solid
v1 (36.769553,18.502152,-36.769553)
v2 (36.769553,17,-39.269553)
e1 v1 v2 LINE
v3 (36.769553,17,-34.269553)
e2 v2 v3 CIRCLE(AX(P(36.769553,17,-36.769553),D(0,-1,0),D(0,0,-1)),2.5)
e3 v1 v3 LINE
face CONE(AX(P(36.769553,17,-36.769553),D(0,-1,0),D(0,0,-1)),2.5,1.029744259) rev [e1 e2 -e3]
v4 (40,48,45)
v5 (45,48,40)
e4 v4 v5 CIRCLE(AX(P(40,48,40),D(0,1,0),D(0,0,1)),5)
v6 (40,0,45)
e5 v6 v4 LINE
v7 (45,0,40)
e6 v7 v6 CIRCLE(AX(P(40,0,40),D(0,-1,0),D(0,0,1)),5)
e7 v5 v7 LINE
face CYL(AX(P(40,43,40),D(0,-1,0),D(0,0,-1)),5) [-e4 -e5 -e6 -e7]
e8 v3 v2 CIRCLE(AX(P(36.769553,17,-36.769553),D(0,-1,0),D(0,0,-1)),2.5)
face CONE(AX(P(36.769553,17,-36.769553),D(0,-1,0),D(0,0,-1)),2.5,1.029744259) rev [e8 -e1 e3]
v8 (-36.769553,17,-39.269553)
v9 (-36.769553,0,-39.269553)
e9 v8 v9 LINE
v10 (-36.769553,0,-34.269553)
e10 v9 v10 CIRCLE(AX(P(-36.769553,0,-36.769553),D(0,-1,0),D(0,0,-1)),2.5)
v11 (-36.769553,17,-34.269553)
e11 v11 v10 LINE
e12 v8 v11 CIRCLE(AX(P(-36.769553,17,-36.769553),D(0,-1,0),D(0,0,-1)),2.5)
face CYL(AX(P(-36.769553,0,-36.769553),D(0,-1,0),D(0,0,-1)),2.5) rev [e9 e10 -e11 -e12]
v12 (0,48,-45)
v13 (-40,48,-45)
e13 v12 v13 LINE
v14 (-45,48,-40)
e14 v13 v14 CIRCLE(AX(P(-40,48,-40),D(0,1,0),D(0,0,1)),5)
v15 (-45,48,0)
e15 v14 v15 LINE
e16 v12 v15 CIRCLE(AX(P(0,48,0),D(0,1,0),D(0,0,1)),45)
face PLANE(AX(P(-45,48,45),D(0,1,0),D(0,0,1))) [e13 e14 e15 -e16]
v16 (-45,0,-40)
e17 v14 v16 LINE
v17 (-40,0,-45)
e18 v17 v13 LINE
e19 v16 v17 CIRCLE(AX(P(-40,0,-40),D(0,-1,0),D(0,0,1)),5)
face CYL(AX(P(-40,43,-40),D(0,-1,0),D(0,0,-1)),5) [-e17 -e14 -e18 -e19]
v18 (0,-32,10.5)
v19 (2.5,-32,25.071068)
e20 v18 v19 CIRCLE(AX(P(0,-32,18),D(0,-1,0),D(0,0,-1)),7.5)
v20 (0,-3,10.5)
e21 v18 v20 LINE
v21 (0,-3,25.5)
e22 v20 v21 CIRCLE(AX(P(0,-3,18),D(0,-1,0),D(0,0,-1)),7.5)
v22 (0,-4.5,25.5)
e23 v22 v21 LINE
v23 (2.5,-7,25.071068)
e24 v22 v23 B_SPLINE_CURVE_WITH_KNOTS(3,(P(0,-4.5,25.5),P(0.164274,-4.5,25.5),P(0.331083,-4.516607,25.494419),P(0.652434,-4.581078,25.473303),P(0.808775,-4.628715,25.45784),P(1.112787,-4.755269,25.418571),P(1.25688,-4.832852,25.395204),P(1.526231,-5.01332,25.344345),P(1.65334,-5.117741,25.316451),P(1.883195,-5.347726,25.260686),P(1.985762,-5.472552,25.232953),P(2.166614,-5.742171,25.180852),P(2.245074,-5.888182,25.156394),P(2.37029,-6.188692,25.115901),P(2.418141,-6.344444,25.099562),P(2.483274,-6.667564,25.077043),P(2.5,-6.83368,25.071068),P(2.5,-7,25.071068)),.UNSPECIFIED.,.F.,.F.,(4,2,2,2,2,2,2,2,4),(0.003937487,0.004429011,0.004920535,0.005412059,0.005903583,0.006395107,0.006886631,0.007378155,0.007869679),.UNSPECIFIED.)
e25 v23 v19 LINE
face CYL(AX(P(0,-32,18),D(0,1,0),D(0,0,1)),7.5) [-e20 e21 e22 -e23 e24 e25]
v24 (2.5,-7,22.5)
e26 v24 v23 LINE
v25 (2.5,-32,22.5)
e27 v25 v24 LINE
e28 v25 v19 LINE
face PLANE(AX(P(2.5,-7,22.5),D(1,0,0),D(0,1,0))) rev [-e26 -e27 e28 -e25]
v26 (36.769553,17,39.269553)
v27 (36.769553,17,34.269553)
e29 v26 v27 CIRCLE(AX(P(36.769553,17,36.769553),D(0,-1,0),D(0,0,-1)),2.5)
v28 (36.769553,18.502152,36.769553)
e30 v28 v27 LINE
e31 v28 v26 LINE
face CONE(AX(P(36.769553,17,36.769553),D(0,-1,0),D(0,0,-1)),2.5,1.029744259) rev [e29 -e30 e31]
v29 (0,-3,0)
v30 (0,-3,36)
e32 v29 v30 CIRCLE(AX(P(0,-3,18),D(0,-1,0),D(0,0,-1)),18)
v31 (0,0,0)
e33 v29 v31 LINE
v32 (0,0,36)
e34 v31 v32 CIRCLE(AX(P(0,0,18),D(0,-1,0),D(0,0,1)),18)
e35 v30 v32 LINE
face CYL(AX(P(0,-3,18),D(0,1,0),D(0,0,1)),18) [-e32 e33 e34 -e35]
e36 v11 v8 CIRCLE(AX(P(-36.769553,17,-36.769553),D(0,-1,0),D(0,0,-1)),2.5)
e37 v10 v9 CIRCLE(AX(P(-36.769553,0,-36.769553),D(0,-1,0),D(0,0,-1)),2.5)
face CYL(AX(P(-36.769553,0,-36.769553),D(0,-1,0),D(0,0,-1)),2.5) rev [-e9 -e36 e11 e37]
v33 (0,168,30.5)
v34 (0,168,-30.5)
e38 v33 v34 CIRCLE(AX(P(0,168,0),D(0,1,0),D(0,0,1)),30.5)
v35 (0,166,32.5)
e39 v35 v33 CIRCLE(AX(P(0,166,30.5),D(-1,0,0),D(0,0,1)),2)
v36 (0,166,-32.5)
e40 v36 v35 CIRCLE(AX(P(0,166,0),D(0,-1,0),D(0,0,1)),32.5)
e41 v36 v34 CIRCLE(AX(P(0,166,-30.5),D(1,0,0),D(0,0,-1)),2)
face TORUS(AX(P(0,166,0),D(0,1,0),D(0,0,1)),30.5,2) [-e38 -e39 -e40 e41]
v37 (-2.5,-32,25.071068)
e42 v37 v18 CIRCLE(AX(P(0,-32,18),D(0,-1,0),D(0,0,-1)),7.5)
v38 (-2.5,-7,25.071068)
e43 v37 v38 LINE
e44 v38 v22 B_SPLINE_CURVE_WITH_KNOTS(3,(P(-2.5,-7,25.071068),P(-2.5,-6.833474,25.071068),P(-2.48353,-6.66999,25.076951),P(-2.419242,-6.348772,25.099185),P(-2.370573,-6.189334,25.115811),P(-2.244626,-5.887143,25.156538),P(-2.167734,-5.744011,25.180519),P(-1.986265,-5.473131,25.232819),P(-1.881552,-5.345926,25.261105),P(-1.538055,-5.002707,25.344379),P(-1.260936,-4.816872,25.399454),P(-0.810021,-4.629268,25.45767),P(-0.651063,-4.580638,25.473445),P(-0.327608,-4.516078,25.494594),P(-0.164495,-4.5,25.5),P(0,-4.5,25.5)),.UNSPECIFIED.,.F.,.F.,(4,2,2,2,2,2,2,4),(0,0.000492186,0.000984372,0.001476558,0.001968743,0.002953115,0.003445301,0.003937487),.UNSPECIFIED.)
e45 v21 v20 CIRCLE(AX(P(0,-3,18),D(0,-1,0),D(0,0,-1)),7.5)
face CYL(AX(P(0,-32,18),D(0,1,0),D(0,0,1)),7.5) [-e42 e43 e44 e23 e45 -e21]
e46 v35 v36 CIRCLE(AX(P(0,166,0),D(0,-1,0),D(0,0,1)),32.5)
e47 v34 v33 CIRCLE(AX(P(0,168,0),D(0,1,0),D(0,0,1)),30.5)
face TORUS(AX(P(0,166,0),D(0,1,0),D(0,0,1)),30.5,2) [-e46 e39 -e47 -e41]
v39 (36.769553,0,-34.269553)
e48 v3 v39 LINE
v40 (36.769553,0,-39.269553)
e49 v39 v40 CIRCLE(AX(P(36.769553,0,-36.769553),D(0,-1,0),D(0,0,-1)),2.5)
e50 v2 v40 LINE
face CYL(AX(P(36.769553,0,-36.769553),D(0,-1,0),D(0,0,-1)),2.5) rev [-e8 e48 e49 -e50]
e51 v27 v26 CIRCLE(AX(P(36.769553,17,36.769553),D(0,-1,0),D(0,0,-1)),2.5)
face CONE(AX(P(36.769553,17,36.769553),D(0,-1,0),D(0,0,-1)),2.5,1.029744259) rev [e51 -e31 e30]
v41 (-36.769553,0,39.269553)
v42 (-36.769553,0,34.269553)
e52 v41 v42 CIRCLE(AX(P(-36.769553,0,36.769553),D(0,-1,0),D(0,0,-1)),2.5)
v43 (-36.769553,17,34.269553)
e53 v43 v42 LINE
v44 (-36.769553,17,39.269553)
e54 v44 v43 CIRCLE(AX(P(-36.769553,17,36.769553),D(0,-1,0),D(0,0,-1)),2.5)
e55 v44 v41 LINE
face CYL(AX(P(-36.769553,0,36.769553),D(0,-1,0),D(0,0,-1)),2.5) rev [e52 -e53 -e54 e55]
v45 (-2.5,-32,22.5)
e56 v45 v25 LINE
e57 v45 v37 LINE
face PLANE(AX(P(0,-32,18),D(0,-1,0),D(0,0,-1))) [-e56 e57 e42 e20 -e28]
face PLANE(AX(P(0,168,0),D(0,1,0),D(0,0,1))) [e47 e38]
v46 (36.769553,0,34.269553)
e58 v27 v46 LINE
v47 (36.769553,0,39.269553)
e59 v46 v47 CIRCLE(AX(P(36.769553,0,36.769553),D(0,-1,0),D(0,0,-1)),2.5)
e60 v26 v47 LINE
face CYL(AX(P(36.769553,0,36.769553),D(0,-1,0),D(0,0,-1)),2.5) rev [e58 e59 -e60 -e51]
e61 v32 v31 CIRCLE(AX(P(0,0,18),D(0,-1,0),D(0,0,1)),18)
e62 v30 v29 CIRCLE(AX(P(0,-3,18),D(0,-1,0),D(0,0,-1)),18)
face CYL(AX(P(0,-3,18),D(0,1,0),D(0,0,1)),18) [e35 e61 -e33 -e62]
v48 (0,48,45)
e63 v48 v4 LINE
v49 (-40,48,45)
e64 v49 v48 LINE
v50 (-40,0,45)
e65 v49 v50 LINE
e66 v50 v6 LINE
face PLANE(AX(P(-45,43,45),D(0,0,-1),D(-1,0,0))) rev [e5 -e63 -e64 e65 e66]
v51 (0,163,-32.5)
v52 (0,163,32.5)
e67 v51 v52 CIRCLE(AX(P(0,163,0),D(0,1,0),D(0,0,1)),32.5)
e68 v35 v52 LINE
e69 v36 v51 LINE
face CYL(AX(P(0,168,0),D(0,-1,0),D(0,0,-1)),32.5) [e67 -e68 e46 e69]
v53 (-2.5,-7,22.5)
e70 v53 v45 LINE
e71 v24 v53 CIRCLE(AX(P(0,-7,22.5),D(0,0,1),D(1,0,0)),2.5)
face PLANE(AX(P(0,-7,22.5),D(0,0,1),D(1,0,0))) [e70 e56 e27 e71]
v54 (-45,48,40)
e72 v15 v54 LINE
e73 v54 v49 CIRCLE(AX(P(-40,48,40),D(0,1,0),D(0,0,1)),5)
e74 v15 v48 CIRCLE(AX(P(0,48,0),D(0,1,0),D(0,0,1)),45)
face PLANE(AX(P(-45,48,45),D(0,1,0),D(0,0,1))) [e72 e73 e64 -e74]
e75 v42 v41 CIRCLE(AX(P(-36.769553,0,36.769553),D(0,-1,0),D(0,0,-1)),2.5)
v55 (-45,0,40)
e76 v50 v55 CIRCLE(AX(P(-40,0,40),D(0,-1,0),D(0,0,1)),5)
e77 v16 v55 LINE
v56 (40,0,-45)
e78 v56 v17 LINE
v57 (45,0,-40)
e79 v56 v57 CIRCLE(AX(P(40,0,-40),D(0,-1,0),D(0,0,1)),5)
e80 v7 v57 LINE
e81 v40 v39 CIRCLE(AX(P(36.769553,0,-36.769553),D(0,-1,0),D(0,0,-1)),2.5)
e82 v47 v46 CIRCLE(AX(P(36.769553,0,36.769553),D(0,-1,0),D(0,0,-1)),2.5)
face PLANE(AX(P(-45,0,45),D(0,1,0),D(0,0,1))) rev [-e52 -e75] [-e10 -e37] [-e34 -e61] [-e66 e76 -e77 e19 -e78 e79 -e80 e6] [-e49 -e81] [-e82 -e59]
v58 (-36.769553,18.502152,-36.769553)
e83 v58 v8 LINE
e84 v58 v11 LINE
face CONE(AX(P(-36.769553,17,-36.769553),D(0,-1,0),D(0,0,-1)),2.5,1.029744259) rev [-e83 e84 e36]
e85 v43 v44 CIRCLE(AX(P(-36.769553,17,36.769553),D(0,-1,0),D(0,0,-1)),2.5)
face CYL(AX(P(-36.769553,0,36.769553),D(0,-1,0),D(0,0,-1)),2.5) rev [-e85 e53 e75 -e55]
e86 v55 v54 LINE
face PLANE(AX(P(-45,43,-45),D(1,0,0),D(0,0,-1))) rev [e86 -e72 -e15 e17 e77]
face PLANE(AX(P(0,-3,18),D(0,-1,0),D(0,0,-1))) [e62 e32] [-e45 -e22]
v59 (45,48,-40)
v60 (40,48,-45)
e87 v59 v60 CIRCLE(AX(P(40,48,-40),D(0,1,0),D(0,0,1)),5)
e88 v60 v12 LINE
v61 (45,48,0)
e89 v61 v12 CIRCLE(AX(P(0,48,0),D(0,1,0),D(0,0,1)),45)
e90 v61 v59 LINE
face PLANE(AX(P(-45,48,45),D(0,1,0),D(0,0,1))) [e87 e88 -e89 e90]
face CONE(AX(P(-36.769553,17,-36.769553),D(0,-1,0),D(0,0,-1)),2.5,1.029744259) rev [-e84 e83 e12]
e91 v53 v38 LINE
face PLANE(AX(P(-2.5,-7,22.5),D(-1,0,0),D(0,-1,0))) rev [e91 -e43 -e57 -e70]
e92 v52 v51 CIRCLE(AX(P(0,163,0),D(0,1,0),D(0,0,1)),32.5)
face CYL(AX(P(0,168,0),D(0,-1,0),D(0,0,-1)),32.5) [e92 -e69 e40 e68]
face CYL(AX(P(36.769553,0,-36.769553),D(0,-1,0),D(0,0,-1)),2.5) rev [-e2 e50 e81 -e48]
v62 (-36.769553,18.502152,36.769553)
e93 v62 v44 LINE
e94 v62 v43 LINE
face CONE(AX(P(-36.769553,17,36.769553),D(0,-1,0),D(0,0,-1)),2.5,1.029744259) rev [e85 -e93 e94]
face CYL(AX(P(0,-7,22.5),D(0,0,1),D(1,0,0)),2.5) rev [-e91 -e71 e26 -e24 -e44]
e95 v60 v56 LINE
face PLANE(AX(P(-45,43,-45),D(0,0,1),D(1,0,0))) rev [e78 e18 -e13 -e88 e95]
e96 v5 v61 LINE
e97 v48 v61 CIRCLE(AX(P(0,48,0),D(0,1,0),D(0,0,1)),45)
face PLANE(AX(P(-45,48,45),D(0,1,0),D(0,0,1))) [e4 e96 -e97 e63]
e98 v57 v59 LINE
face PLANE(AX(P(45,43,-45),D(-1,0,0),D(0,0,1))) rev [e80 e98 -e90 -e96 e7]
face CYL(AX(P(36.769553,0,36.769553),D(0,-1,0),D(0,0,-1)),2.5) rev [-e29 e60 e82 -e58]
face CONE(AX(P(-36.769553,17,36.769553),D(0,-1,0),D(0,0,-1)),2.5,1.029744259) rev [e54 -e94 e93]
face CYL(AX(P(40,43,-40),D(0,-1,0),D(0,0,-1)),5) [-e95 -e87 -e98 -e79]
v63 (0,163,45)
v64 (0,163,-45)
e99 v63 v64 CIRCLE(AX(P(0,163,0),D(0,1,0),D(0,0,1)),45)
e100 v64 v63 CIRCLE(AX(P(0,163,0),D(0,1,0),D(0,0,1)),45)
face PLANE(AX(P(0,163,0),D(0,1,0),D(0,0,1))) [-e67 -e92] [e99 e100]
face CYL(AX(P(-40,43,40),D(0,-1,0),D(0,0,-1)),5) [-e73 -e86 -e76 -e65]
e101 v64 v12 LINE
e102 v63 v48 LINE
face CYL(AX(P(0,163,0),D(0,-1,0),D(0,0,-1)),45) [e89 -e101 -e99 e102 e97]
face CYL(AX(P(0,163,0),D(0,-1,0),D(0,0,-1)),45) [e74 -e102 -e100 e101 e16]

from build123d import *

# Parameters (mm, degrees)
SKETCH_1_W               = 90
SKETCH_1_H               = 90
EXTRUDE_1_DEPTH          = 43
SKETCH_2_R               = 18
EXTRUDE_2_DEPTH          = 3
SKETCH_3_R               = 7.5
EXTRUDE_3_DEPTH          = 29
CUT_EXTRUDE_1_DEPTH      = 3
PATTERN_CIRCULAR_1_COUNT = 4
SKETCH_8_R               = 45
EXTRUDE_4_DEPTH          = 120
SKETCH_9_R               = 32.5
EXTRUDE_5_DEPTH          = 5
SKETCH_10_W              = 90
SKETCH_10_H              = 90
EXTRUDE_6_DEPTH          = 5
FILLET_1_R               = 5
FILLET_2_R               = 2


with BuildPart() as part:
    # 草图1 → 凸台-拉伸1 (new body)
    with BuildSketch(Plane(origin=(0, 0, 0), x_dir=(1, 0, 0), z_dir=(0, 1, 0))):
        Rectangle(SKETCH_1_W, SKETCH_1_H)
    extrude(amount=EXTRUDE_1_DEPTH)

    # 草图2 → 凸台-拉伸2 (add)
    with BuildSketch(Plane.XZ):
        with Locations(Location((0, 18, 0), (0, 0, 90))):
            Circle(SKETCH_2_R)
    extrude(amount=EXTRUDE_2_DEPTH)

    # 草图3 → 凸台-拉伸3 (add)
    with BuildSketch(Plane.XZ.offset(3)):
        with Locations(Location((0, 18, 0), (0, 0, 90))):
            Circle(SKETCH_3_R)
    extrude(amount=EXTRUDE_3_DEPTH)

    # 草图4 → 切除-拉伸1 (cut)
    with BuildSketch(Plane.XY.offset(25.5)):
        with BuildLine():
            Line((-2.5, -7), (-2.5, -32))
            Line((-2.5, -32), (2.5, -32))
            Line((2.5, -32), (2.5, -7))
            ThreePointArc((2.5, -7), (0, -4.5), (-2.5, -7))
        make_face()
    extrude(amount=-CUT_EXTRUDE_1_DEPTH, mode=Mode.SUBTRACT)

    # 草图6 → M6x1.0 螺纹孔1 (revolve, cut)
    with BuildSketch(Plane(origin=(36.769552622, 0, 36.769552622), x_dir=(0, 0, -1), z_dir=(1, 0, 0))):
        Polygon((0, 0), (0, 18.502151548), (2.5, 17), (2.5, 0), align=None)
    m6x1_0_1 = revolve(axis=Axis((36.769552622, -6.35, 36.769552622), (0, 1, 0)), mode=Mode.SUBTRACT)

    # 阵列(圆周)1: M6x1.0 螺纹孔1 ×4 about axis
    pattern_circular_1_axis = Axis((0, 0, 0), (0, 1, 0))
    for i in range(1, PATTERN_CIRCULAR_1_COUNT):
        add(m6x1_0_1.rotate(pattern_circular_1_axis, i * 360 / PATTERN_CIRCULAR_1_COUNT), mode=Mode.SUBTRACT)

    # 草图8 → 凸台-拉伸4 (add)
    with BuildSketch(Plane(origin=(0, 43, 0), x_dir=(1, 0, 0), z_dir=(0, 1, 0))):
        with Locations(Location((0, 0, 0), (0, 0, 270))):
            Circle(SKETCH_8_R)
    extrude(amount=EXTRUDE_4_DEPTH)

    # 草图9 → 凸台-拉伸5 (add)
    with BuildSketch(Plane(origin=(0, 163, 0), x_dir=(1, 0, 0), z_dir=(0, 1, 0))):
        with Locations(Location((0, 0, 0), (0, 0, 270))):
            Circle(SKETCH_9_R)
    extrude(amount=EXTRUDE_5_DEPTH)

    # 草图10 → 凸台-拉伸6 (add)
    with BuildSketch(Plane(origin=(0, 43, 0), x_dir=(1, 0, 0), z_dir=(0, 1, 0))):
        Rectangle(SKETCH_10_W, SKETCH_10_H)
    extrude(amount=EXTRUDE_6_DEPTH)

    # 圆角1
    fillet_1_edges = [part.edges().sort_by_distance(p)[0] for p in [
        (-45, 24, -45),
        (45, 24, -45),
        (45, 24, 45),
        (-45, 24, 45),
    ]]
    fillet(fillet_1_edges, radius=FILLET_1_R)

    # 圆角2
    fillet_2_edges = [part.edges().sort_by_distance(p)[0] for p in [
        (0, 168, -32.5),
    ]]
    fillet(fillet_2_edges, radius=FILLET_2_R)


solid = part.part
